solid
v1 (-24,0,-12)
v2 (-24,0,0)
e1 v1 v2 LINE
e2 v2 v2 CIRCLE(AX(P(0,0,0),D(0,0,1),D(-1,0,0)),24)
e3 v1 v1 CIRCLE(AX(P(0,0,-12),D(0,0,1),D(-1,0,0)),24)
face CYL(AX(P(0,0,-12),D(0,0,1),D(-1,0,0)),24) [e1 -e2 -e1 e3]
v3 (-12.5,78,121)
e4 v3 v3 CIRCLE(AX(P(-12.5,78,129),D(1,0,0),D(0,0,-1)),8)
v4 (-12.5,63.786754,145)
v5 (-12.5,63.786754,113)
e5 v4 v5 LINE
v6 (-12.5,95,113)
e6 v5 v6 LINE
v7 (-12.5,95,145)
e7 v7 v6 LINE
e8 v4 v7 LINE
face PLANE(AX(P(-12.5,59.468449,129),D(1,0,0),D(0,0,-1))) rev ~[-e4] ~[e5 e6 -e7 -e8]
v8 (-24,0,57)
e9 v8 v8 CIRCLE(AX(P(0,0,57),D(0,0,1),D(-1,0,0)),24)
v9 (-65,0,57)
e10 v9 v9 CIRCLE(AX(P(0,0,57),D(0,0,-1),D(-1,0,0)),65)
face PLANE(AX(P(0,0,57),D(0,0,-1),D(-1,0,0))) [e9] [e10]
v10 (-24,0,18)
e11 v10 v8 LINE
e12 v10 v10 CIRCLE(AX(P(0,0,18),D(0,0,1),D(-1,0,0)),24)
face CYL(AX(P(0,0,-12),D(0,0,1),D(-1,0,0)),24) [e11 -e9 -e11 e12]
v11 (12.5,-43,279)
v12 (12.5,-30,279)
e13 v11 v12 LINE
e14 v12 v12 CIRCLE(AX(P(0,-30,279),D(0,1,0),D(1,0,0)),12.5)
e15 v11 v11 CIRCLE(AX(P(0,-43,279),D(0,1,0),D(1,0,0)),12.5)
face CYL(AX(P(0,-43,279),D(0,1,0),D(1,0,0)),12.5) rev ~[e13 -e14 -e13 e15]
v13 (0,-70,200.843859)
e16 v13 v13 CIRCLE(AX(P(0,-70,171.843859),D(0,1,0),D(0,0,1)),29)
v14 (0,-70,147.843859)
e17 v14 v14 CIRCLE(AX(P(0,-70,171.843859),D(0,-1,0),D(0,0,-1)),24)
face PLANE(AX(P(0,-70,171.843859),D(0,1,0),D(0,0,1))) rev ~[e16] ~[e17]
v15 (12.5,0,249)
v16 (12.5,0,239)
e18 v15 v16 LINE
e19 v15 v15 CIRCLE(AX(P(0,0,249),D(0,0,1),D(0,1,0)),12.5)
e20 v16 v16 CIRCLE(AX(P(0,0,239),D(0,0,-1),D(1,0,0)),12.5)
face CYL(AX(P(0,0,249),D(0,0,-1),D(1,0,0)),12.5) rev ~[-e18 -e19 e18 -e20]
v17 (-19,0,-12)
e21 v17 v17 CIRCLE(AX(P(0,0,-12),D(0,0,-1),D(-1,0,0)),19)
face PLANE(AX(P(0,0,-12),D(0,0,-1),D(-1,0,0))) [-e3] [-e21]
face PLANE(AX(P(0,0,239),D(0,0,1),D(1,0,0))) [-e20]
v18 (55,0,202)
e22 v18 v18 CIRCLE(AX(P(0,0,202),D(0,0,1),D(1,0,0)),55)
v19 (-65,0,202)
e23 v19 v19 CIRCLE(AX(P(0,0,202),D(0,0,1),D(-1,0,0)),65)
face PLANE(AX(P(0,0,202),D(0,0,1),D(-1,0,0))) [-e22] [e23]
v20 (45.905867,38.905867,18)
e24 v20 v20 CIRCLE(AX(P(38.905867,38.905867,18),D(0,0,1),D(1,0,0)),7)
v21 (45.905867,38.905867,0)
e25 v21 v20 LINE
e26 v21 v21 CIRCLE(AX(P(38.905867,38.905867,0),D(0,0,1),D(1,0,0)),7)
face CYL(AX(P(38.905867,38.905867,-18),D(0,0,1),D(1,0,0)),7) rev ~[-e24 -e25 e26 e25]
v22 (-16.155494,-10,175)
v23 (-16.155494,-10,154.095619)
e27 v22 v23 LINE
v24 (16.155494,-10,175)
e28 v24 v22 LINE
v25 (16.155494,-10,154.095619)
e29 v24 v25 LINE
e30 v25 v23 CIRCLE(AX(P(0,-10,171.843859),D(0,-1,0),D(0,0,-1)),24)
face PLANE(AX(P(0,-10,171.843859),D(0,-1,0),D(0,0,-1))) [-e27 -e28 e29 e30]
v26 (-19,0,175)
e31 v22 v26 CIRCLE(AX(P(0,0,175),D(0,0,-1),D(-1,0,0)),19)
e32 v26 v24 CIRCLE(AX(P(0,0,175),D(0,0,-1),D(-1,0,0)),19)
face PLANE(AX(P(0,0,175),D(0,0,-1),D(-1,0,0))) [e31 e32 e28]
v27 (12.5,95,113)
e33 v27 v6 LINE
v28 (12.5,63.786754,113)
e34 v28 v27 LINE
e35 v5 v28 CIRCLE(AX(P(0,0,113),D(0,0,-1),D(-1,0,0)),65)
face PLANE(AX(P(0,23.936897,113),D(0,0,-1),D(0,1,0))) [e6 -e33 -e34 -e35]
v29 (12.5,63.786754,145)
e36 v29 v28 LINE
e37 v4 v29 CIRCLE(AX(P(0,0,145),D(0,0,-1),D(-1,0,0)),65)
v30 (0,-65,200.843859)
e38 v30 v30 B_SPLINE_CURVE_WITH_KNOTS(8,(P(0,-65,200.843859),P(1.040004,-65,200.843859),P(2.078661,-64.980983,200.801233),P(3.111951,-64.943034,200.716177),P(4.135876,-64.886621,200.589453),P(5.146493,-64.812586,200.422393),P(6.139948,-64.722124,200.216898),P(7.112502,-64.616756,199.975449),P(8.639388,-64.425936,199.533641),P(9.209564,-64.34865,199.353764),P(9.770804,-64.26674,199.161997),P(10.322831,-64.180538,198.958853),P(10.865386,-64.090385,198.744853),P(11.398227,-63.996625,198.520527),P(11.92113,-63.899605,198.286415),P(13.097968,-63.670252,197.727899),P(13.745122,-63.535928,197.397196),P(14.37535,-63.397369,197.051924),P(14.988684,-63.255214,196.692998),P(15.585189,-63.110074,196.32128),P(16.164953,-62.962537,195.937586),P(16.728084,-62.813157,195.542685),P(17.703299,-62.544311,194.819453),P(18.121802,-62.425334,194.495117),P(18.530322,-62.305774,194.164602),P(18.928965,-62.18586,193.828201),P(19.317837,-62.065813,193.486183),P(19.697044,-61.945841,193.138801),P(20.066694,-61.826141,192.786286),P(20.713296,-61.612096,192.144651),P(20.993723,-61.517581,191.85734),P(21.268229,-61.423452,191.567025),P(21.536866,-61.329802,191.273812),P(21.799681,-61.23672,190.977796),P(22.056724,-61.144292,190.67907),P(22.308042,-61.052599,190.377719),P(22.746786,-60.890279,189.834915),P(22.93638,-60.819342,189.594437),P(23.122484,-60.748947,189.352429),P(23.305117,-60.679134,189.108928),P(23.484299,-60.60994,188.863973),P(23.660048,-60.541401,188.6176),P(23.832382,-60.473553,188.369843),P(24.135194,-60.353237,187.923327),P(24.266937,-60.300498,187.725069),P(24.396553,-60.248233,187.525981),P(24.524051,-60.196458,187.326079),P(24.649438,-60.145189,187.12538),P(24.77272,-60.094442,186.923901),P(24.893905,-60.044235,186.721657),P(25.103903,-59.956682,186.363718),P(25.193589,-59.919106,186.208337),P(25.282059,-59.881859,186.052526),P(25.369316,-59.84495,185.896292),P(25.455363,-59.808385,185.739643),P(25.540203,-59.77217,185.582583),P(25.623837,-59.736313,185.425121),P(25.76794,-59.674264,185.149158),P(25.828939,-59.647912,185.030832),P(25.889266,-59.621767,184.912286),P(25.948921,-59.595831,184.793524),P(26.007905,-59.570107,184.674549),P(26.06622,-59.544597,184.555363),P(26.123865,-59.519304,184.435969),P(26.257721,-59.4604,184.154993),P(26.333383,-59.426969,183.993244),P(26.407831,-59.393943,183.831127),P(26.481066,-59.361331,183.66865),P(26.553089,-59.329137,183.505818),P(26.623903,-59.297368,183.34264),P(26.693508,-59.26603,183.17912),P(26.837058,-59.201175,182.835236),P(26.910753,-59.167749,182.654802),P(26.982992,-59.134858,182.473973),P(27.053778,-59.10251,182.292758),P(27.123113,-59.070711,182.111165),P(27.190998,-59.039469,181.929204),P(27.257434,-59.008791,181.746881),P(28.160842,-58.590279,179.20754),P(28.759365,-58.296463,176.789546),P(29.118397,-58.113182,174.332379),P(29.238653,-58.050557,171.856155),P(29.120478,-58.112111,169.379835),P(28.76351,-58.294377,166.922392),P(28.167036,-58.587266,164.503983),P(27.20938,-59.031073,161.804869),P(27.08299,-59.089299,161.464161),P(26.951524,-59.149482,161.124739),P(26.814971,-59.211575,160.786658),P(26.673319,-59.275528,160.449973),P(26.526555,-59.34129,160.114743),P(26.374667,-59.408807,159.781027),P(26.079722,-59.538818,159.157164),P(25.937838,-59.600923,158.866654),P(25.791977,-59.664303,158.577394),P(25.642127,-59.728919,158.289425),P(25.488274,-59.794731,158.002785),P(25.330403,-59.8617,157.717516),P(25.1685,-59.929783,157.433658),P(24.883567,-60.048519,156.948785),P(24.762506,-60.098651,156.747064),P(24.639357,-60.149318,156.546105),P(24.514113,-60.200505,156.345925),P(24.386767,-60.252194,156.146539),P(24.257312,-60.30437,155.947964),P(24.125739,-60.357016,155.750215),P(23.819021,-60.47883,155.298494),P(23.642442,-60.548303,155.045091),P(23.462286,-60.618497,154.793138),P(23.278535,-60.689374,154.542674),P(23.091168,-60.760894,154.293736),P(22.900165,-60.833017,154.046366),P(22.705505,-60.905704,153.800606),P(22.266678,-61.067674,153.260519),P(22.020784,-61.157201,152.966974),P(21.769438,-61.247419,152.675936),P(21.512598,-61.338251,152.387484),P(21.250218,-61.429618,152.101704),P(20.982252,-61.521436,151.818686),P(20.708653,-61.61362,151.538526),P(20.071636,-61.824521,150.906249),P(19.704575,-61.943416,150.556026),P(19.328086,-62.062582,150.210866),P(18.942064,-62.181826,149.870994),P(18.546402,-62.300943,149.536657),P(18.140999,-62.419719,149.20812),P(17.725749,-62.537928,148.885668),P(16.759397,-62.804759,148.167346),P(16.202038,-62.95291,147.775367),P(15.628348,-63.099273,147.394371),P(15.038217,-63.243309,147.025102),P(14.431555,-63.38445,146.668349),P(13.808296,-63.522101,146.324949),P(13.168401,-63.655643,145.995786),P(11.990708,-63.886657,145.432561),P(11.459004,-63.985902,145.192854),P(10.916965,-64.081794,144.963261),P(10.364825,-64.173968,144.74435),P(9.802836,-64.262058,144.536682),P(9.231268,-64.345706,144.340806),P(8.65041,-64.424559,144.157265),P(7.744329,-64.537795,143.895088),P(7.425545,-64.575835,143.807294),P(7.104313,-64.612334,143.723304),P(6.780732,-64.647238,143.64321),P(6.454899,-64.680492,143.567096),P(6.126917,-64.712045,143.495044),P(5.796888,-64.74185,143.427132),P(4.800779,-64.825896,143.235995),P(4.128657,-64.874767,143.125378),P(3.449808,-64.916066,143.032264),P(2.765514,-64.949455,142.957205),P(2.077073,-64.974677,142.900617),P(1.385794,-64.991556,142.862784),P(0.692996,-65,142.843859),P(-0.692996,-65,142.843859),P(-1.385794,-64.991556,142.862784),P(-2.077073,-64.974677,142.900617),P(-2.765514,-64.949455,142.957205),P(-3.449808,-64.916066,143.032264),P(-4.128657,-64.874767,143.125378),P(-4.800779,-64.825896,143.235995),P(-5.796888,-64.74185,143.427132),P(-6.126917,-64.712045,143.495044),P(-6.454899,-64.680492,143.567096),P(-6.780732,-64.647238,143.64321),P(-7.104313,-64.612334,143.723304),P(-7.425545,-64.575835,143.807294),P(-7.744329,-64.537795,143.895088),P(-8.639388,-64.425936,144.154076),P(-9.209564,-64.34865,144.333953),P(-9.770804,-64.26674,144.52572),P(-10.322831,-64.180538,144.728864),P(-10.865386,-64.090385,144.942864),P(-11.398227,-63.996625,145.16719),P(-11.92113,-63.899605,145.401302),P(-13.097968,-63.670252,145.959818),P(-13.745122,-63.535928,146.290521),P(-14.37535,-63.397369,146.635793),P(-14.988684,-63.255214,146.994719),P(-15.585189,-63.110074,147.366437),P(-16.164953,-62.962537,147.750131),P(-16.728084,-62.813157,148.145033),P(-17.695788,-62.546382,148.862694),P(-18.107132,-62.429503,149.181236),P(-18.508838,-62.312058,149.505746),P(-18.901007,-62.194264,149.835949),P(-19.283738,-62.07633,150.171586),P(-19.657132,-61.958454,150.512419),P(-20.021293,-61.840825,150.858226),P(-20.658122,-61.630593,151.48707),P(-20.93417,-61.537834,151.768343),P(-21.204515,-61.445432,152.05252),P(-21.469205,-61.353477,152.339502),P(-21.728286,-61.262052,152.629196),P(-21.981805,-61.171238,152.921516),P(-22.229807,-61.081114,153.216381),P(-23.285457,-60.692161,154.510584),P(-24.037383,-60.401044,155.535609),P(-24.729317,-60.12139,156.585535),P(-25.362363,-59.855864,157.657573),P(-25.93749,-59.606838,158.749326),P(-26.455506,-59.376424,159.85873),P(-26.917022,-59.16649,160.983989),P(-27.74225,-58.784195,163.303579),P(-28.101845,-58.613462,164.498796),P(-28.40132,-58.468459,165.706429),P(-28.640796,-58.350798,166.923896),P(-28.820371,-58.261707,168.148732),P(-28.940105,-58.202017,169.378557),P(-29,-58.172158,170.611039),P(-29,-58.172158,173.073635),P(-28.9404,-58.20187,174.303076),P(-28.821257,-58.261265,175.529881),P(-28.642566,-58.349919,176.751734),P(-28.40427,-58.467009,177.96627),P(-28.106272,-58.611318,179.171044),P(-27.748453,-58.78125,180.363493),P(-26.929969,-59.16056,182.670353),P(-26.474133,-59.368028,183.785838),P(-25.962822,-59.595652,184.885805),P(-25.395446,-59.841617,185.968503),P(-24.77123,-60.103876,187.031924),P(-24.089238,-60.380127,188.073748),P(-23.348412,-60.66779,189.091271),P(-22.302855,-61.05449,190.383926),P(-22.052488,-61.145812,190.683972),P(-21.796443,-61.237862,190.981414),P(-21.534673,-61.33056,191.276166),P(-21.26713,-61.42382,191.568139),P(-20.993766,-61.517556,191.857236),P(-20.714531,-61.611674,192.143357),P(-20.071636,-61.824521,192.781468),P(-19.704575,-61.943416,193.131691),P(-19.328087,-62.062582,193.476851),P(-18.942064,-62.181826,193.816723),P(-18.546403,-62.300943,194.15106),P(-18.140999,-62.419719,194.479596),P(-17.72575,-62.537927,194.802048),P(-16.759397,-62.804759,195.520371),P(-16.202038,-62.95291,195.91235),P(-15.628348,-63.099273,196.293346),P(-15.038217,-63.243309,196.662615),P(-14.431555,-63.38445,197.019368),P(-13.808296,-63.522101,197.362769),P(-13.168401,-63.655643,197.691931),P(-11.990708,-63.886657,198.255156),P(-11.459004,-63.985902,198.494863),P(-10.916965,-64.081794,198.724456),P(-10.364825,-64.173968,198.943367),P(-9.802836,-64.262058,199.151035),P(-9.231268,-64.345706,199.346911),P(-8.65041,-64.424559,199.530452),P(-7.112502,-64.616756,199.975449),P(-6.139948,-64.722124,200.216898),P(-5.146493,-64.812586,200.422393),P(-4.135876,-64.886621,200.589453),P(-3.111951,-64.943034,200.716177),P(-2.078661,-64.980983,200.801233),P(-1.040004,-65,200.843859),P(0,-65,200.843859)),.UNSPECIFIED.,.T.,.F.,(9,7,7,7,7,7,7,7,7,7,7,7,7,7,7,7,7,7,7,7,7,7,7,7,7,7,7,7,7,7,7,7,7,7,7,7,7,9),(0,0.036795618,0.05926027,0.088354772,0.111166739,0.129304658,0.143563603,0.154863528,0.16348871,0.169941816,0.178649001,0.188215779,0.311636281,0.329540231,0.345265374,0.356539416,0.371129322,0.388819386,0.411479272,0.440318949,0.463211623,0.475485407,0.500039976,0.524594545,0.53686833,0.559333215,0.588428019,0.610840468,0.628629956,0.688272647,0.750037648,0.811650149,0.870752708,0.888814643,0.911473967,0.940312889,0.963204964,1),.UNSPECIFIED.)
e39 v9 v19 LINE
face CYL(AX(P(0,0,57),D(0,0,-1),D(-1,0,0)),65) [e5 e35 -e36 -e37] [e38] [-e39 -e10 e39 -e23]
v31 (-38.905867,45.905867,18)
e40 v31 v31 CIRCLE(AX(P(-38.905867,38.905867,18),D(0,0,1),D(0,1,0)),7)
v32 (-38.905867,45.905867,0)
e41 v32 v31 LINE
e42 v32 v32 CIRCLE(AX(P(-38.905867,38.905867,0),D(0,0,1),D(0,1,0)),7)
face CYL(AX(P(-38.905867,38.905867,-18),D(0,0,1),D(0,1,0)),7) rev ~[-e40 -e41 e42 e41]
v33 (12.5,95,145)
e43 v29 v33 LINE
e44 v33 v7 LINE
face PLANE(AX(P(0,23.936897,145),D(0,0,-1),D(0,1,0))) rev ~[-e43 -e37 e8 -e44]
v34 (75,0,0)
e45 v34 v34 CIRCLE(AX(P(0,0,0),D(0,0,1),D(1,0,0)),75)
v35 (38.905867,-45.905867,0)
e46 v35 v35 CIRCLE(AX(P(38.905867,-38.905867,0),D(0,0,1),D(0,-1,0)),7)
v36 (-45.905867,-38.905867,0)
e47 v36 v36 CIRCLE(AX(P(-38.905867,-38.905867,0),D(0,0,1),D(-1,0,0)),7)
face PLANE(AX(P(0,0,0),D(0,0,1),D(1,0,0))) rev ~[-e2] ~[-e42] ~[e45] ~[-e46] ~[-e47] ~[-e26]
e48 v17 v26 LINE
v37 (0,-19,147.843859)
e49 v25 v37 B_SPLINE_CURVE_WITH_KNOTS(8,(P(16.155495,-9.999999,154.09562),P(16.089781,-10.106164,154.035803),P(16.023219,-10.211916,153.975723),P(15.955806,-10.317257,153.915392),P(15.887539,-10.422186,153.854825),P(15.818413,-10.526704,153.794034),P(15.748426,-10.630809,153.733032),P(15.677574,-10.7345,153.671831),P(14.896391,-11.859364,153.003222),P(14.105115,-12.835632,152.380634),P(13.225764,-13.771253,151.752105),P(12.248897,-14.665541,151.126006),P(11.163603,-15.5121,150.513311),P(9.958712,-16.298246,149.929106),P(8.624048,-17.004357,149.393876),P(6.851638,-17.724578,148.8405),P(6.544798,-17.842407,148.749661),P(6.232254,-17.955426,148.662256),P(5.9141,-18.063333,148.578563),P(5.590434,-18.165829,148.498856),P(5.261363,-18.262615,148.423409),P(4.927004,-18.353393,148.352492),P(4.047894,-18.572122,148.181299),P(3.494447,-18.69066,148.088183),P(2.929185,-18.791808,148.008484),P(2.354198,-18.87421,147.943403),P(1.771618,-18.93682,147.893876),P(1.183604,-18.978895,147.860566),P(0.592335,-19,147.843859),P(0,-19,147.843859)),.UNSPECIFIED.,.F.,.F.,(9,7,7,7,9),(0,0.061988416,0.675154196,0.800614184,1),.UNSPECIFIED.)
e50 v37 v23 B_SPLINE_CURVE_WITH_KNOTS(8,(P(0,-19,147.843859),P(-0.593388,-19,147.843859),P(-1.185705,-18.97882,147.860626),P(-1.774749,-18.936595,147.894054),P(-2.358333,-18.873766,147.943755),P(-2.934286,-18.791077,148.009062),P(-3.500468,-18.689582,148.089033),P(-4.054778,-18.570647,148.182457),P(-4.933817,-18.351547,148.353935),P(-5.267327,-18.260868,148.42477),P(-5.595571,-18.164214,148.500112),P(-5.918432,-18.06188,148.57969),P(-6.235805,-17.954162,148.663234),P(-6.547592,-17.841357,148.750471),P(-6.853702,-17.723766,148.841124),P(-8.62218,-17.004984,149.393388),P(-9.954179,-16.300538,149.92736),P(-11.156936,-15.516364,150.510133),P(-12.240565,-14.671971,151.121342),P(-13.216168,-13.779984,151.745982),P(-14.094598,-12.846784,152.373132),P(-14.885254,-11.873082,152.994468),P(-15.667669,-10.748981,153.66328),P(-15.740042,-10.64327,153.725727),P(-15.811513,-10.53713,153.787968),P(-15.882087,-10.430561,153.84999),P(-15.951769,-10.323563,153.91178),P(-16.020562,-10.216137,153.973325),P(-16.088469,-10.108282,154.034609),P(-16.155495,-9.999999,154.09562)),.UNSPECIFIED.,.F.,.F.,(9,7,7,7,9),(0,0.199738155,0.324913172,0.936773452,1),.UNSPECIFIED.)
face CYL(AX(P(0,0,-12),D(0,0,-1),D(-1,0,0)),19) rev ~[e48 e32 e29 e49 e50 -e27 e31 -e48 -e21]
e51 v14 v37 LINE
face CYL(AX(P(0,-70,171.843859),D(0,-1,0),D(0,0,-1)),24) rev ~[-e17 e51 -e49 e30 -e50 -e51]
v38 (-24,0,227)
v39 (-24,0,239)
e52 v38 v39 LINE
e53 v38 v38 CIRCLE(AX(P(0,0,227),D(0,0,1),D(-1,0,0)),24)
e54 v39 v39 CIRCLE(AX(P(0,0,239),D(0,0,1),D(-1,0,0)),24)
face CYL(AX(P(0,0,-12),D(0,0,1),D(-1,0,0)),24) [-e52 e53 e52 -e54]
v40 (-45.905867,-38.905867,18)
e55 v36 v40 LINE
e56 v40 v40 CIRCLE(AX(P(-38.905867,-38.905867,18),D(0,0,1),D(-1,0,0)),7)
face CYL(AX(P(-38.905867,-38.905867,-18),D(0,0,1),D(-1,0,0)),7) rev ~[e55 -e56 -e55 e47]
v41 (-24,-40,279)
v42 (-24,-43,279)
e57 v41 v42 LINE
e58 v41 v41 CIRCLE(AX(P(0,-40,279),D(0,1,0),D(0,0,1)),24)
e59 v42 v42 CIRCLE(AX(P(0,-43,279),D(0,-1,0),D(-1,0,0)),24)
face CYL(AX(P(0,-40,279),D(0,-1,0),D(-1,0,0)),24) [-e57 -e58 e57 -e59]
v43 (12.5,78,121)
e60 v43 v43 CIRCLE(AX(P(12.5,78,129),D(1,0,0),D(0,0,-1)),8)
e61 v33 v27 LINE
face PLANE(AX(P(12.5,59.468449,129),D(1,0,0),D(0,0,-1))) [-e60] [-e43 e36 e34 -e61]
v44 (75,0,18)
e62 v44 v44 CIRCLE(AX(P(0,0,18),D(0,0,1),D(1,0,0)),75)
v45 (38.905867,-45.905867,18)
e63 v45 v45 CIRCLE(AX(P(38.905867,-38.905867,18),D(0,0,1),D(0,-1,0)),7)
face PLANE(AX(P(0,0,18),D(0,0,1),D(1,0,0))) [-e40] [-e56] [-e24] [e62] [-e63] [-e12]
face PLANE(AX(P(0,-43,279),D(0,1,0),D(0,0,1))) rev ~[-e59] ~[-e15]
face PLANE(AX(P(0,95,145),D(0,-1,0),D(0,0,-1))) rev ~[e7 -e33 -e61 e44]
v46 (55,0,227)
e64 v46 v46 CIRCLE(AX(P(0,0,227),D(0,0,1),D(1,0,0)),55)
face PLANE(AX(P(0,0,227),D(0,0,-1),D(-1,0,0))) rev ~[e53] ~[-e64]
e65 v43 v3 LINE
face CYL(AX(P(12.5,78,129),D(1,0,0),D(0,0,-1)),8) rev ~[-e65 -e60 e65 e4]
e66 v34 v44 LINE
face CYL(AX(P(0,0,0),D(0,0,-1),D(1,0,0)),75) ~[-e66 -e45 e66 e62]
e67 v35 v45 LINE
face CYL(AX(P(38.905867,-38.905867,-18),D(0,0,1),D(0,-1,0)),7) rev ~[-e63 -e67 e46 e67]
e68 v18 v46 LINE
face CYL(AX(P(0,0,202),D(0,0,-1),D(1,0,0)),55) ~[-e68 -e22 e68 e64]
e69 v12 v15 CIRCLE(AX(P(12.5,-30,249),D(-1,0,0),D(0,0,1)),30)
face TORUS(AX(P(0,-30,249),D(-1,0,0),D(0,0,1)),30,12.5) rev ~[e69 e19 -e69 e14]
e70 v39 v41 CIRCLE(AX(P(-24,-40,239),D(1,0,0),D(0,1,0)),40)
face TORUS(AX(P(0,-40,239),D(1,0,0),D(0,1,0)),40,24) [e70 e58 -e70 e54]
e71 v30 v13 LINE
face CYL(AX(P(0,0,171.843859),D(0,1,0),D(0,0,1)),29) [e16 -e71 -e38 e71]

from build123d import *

# Parameters (mm, degrees)
SKETCH1_R             = 75
BOSS_EXTRUDE1_DEPTH   = 18
SKETCH2_R             = 24
CUT_EXTRUDE1_DEPTH    = 12
SKETCH5_R             = 24
SKETCH6_R             = 65
BOSS_EXTRUDE2_DEPTH   = 170
F_14_0_14_HOLE1_D     = 14
F_14_0_14_HOLE1_DEPTH = 18
CIRPATTERN1_COUNT     = 4
SKETCH10_R            = 29
BOSS_EXTRUDE3_DEPTH   = 70
SKETCH11_R            = 19
CUT_EXTRUDE2_DEPTH    = 187
SKETCH13_R            = 12.5
CUT_EXTRUDE3_START    = -25
SKETCH14_R            = 65
SKETCH14_R_2          = 55
CUT_EXTRUDE3_DEPTH    = 25
SKETCH15_R            = 24
CUT_EXTRUDE4_DEPTH    = 60
SKETCH16_W            = 32
SKETCH16_H            = 71.063102747
BOSS_EXTRUDE4_DEPTH   = 12.5
SKETCH17_R            = 8
CUT_EXTRUDE5_DEPTH    = 25


with BuildPart() as part:
    # Sketch1 → Boss-Extrude1 (new body)
    with BuildSketch(Plane.XY):
        Circle(SKETCH1_R)
    extrude(amount=BOSS_EXTRUDE1_DEPTH)

    # Sketch2 → Cut-Extrude1 (cut)
    with BuildSketch(Plane.XY.offset(18)):
        Circle(SKETCH2_R)
    extrude(amount=-CUT_EXTRUDE1_DEPTH, mode=Mode.SUBTRACT)

    # Sweep1: sweep along a path in Sketch3
    with BuildLine(Plane(origin=(0, 0, 0), x_dir=(0, 0, -1), z_dir=(1, 0, 0))) as sweep1_path:
        Line((12, 0), (-239, 0))
        ThreePointArc((-239, 0), (-267.284271247, -11.715728753), (-279, -40))
        Line((-279, -40), (-279, -43))
    # Sketch5 → Sweep1 (sweep)
    with BuildSketch(Plane(origin=(0, 0, -12), x_dir=(-1, 0, 0), z_dir=(0, 0, -1))):
        Circle(SKETCH5_R)
    sweep(path=sweep1_path.line)

    # Sketch6 → Boss-Extrude2 (add)
    with BuildSketch(Plane(origin=(0, 0, 57), x_dir=(-1, 0, 0), z_dir=(0, 0, -1))):
        Circle(SKETCH6_R)
    extrude(amount=-BOSS_EXTRUDE2_DEPTH)

    # Ø14.0 (14) Hole1
    with Locations(Plane(origin=(0, 0, 0), x_dir=(-1, 0, 0), z_dir=(0, 0, -1))):
        with Locations((-38.905866791, 38.905866791)):
            f_14_0_14_hole1 = Hole(F_14_0_14_HOLE1_D / 2, depth=F_14_0_14_HOLE1_DEPTH)

    # CirPattern1: Ø14.0 (14) Hole1 ×4 about axis
    cirpattern1_axis = Axis((0, 0, 0), (0, 0, 1))
    for i in range(1, CIRPATTERN1_COUNT):
        add(f_14_0_14_hole1.rotate(cirpattern1_axis, i * 360 / CIRPATTERN1_COUNT), mode=Mode.SUBTRACT)

    # Sketch10 → Boss-Extrude3 (add)
    with BuildSketch(Plane(origin=(0, 0, 0), x_dir=(1, 0, 0), z_dir=(0, 1, 0))):
        with Locations(Location((0, -171.843858555, 0), (0, 0, 270))):
            Circle(SKETCH10_R)
    extrude(amount=-BOSS_EXTRUDE3_DEPTH)

    # Sketch11 → Cut-Extrude2 (cut)
    with BuildSketch(Plane(origin=(0, 0, -12), x_dir=(-1, 0, 0), z_dir=(0, 0, -1))):
        Circle(SKETCH11_R)
    extrude(amount=-CUT_EXTRUDE2_DEPTH, mode=Mode.SUBTRACT)

    # Cut-Sweep1: sweep along a path in Sketch12
    with BuildLine(Plane(origin=(0, 0, 0), x_dir=(0, 0, -1), z_dir=(1, 0, 0))) as cut_sweep1_path:
        Line((-279, -43), (-279, -30))
        ThreePointArc((-279, -30), (-270.213203436, -8.786796564), (-249, 0))
        Line((-249, 0), (-239, 0))
    # Sketch13 → Cut-Sweep1 (sweep, cut)
    with BuildSketch(Plane.XZ.offset(43)):
        with Locations((0, 279)):
            Circle(SKETCH13_R)
    sweep(path=cut_sweep1_path.line, mode=Mode.SUBTRACT)

    # Sketch14 → Cut-Extrude3 (cut)
    with BuildSketch(Plane.XY.offset(227).offset(CUT_EXTRUDE3_START)):
        with Locations(Location((0, 0, 0), (0, 0, 180))):
            Circle(SKETCH14_R)
        Circle(SKETCH14_R_2, mode=Mode.SUBTRACT)
    extrude(amount=CUT_EXTRUDE3_DEPTH, mode=Mode.SUBTRACT)

    # Sketch15 → Cut-Extrude4 (cut)
    with BuildSketch(Plane(origin=(0, -70, 0), x_dir=(-1, 0, 0), z_dir=(0, -1, 0))):
        with Locations(Location((0, -171.843858555, 0), (0, 0, 90))):
            Circle(SKETCH15_R)
    extrude(amount=-CUT_EXTRUDE4_DEPTH, mode=Mode.SUBTRACT)

    # Sketch16 → Boss-Extrude4 (add, symmetric)
    with BuildSketch(Plane(origin=(0, 0, 0), x_dir=(0, 0, -1), z_dir=(1, 0, 0))):
        with Locations((-129, 59.468448626)):
            Rectangle(SKETCH16_W, SKETCH16_H)
    extrude(amount=BOSS_EXTRUDE4_DEPTH, both=True)

    # Sketch17 → Cut-Extrude5 (cut)
    with BuildSketch(Plane(origin=(12.5, 0, 0), x_dir=(0, 0, -1), z_dir=(1, 0, 0))):
        with Locations((-129, 78)):
            Circle(SKETCH17_R)
    extrude(amount=-CUT_EXTRUDE5_DEPTH, mode=Mode.SUBTRACT)


solid = part.part
